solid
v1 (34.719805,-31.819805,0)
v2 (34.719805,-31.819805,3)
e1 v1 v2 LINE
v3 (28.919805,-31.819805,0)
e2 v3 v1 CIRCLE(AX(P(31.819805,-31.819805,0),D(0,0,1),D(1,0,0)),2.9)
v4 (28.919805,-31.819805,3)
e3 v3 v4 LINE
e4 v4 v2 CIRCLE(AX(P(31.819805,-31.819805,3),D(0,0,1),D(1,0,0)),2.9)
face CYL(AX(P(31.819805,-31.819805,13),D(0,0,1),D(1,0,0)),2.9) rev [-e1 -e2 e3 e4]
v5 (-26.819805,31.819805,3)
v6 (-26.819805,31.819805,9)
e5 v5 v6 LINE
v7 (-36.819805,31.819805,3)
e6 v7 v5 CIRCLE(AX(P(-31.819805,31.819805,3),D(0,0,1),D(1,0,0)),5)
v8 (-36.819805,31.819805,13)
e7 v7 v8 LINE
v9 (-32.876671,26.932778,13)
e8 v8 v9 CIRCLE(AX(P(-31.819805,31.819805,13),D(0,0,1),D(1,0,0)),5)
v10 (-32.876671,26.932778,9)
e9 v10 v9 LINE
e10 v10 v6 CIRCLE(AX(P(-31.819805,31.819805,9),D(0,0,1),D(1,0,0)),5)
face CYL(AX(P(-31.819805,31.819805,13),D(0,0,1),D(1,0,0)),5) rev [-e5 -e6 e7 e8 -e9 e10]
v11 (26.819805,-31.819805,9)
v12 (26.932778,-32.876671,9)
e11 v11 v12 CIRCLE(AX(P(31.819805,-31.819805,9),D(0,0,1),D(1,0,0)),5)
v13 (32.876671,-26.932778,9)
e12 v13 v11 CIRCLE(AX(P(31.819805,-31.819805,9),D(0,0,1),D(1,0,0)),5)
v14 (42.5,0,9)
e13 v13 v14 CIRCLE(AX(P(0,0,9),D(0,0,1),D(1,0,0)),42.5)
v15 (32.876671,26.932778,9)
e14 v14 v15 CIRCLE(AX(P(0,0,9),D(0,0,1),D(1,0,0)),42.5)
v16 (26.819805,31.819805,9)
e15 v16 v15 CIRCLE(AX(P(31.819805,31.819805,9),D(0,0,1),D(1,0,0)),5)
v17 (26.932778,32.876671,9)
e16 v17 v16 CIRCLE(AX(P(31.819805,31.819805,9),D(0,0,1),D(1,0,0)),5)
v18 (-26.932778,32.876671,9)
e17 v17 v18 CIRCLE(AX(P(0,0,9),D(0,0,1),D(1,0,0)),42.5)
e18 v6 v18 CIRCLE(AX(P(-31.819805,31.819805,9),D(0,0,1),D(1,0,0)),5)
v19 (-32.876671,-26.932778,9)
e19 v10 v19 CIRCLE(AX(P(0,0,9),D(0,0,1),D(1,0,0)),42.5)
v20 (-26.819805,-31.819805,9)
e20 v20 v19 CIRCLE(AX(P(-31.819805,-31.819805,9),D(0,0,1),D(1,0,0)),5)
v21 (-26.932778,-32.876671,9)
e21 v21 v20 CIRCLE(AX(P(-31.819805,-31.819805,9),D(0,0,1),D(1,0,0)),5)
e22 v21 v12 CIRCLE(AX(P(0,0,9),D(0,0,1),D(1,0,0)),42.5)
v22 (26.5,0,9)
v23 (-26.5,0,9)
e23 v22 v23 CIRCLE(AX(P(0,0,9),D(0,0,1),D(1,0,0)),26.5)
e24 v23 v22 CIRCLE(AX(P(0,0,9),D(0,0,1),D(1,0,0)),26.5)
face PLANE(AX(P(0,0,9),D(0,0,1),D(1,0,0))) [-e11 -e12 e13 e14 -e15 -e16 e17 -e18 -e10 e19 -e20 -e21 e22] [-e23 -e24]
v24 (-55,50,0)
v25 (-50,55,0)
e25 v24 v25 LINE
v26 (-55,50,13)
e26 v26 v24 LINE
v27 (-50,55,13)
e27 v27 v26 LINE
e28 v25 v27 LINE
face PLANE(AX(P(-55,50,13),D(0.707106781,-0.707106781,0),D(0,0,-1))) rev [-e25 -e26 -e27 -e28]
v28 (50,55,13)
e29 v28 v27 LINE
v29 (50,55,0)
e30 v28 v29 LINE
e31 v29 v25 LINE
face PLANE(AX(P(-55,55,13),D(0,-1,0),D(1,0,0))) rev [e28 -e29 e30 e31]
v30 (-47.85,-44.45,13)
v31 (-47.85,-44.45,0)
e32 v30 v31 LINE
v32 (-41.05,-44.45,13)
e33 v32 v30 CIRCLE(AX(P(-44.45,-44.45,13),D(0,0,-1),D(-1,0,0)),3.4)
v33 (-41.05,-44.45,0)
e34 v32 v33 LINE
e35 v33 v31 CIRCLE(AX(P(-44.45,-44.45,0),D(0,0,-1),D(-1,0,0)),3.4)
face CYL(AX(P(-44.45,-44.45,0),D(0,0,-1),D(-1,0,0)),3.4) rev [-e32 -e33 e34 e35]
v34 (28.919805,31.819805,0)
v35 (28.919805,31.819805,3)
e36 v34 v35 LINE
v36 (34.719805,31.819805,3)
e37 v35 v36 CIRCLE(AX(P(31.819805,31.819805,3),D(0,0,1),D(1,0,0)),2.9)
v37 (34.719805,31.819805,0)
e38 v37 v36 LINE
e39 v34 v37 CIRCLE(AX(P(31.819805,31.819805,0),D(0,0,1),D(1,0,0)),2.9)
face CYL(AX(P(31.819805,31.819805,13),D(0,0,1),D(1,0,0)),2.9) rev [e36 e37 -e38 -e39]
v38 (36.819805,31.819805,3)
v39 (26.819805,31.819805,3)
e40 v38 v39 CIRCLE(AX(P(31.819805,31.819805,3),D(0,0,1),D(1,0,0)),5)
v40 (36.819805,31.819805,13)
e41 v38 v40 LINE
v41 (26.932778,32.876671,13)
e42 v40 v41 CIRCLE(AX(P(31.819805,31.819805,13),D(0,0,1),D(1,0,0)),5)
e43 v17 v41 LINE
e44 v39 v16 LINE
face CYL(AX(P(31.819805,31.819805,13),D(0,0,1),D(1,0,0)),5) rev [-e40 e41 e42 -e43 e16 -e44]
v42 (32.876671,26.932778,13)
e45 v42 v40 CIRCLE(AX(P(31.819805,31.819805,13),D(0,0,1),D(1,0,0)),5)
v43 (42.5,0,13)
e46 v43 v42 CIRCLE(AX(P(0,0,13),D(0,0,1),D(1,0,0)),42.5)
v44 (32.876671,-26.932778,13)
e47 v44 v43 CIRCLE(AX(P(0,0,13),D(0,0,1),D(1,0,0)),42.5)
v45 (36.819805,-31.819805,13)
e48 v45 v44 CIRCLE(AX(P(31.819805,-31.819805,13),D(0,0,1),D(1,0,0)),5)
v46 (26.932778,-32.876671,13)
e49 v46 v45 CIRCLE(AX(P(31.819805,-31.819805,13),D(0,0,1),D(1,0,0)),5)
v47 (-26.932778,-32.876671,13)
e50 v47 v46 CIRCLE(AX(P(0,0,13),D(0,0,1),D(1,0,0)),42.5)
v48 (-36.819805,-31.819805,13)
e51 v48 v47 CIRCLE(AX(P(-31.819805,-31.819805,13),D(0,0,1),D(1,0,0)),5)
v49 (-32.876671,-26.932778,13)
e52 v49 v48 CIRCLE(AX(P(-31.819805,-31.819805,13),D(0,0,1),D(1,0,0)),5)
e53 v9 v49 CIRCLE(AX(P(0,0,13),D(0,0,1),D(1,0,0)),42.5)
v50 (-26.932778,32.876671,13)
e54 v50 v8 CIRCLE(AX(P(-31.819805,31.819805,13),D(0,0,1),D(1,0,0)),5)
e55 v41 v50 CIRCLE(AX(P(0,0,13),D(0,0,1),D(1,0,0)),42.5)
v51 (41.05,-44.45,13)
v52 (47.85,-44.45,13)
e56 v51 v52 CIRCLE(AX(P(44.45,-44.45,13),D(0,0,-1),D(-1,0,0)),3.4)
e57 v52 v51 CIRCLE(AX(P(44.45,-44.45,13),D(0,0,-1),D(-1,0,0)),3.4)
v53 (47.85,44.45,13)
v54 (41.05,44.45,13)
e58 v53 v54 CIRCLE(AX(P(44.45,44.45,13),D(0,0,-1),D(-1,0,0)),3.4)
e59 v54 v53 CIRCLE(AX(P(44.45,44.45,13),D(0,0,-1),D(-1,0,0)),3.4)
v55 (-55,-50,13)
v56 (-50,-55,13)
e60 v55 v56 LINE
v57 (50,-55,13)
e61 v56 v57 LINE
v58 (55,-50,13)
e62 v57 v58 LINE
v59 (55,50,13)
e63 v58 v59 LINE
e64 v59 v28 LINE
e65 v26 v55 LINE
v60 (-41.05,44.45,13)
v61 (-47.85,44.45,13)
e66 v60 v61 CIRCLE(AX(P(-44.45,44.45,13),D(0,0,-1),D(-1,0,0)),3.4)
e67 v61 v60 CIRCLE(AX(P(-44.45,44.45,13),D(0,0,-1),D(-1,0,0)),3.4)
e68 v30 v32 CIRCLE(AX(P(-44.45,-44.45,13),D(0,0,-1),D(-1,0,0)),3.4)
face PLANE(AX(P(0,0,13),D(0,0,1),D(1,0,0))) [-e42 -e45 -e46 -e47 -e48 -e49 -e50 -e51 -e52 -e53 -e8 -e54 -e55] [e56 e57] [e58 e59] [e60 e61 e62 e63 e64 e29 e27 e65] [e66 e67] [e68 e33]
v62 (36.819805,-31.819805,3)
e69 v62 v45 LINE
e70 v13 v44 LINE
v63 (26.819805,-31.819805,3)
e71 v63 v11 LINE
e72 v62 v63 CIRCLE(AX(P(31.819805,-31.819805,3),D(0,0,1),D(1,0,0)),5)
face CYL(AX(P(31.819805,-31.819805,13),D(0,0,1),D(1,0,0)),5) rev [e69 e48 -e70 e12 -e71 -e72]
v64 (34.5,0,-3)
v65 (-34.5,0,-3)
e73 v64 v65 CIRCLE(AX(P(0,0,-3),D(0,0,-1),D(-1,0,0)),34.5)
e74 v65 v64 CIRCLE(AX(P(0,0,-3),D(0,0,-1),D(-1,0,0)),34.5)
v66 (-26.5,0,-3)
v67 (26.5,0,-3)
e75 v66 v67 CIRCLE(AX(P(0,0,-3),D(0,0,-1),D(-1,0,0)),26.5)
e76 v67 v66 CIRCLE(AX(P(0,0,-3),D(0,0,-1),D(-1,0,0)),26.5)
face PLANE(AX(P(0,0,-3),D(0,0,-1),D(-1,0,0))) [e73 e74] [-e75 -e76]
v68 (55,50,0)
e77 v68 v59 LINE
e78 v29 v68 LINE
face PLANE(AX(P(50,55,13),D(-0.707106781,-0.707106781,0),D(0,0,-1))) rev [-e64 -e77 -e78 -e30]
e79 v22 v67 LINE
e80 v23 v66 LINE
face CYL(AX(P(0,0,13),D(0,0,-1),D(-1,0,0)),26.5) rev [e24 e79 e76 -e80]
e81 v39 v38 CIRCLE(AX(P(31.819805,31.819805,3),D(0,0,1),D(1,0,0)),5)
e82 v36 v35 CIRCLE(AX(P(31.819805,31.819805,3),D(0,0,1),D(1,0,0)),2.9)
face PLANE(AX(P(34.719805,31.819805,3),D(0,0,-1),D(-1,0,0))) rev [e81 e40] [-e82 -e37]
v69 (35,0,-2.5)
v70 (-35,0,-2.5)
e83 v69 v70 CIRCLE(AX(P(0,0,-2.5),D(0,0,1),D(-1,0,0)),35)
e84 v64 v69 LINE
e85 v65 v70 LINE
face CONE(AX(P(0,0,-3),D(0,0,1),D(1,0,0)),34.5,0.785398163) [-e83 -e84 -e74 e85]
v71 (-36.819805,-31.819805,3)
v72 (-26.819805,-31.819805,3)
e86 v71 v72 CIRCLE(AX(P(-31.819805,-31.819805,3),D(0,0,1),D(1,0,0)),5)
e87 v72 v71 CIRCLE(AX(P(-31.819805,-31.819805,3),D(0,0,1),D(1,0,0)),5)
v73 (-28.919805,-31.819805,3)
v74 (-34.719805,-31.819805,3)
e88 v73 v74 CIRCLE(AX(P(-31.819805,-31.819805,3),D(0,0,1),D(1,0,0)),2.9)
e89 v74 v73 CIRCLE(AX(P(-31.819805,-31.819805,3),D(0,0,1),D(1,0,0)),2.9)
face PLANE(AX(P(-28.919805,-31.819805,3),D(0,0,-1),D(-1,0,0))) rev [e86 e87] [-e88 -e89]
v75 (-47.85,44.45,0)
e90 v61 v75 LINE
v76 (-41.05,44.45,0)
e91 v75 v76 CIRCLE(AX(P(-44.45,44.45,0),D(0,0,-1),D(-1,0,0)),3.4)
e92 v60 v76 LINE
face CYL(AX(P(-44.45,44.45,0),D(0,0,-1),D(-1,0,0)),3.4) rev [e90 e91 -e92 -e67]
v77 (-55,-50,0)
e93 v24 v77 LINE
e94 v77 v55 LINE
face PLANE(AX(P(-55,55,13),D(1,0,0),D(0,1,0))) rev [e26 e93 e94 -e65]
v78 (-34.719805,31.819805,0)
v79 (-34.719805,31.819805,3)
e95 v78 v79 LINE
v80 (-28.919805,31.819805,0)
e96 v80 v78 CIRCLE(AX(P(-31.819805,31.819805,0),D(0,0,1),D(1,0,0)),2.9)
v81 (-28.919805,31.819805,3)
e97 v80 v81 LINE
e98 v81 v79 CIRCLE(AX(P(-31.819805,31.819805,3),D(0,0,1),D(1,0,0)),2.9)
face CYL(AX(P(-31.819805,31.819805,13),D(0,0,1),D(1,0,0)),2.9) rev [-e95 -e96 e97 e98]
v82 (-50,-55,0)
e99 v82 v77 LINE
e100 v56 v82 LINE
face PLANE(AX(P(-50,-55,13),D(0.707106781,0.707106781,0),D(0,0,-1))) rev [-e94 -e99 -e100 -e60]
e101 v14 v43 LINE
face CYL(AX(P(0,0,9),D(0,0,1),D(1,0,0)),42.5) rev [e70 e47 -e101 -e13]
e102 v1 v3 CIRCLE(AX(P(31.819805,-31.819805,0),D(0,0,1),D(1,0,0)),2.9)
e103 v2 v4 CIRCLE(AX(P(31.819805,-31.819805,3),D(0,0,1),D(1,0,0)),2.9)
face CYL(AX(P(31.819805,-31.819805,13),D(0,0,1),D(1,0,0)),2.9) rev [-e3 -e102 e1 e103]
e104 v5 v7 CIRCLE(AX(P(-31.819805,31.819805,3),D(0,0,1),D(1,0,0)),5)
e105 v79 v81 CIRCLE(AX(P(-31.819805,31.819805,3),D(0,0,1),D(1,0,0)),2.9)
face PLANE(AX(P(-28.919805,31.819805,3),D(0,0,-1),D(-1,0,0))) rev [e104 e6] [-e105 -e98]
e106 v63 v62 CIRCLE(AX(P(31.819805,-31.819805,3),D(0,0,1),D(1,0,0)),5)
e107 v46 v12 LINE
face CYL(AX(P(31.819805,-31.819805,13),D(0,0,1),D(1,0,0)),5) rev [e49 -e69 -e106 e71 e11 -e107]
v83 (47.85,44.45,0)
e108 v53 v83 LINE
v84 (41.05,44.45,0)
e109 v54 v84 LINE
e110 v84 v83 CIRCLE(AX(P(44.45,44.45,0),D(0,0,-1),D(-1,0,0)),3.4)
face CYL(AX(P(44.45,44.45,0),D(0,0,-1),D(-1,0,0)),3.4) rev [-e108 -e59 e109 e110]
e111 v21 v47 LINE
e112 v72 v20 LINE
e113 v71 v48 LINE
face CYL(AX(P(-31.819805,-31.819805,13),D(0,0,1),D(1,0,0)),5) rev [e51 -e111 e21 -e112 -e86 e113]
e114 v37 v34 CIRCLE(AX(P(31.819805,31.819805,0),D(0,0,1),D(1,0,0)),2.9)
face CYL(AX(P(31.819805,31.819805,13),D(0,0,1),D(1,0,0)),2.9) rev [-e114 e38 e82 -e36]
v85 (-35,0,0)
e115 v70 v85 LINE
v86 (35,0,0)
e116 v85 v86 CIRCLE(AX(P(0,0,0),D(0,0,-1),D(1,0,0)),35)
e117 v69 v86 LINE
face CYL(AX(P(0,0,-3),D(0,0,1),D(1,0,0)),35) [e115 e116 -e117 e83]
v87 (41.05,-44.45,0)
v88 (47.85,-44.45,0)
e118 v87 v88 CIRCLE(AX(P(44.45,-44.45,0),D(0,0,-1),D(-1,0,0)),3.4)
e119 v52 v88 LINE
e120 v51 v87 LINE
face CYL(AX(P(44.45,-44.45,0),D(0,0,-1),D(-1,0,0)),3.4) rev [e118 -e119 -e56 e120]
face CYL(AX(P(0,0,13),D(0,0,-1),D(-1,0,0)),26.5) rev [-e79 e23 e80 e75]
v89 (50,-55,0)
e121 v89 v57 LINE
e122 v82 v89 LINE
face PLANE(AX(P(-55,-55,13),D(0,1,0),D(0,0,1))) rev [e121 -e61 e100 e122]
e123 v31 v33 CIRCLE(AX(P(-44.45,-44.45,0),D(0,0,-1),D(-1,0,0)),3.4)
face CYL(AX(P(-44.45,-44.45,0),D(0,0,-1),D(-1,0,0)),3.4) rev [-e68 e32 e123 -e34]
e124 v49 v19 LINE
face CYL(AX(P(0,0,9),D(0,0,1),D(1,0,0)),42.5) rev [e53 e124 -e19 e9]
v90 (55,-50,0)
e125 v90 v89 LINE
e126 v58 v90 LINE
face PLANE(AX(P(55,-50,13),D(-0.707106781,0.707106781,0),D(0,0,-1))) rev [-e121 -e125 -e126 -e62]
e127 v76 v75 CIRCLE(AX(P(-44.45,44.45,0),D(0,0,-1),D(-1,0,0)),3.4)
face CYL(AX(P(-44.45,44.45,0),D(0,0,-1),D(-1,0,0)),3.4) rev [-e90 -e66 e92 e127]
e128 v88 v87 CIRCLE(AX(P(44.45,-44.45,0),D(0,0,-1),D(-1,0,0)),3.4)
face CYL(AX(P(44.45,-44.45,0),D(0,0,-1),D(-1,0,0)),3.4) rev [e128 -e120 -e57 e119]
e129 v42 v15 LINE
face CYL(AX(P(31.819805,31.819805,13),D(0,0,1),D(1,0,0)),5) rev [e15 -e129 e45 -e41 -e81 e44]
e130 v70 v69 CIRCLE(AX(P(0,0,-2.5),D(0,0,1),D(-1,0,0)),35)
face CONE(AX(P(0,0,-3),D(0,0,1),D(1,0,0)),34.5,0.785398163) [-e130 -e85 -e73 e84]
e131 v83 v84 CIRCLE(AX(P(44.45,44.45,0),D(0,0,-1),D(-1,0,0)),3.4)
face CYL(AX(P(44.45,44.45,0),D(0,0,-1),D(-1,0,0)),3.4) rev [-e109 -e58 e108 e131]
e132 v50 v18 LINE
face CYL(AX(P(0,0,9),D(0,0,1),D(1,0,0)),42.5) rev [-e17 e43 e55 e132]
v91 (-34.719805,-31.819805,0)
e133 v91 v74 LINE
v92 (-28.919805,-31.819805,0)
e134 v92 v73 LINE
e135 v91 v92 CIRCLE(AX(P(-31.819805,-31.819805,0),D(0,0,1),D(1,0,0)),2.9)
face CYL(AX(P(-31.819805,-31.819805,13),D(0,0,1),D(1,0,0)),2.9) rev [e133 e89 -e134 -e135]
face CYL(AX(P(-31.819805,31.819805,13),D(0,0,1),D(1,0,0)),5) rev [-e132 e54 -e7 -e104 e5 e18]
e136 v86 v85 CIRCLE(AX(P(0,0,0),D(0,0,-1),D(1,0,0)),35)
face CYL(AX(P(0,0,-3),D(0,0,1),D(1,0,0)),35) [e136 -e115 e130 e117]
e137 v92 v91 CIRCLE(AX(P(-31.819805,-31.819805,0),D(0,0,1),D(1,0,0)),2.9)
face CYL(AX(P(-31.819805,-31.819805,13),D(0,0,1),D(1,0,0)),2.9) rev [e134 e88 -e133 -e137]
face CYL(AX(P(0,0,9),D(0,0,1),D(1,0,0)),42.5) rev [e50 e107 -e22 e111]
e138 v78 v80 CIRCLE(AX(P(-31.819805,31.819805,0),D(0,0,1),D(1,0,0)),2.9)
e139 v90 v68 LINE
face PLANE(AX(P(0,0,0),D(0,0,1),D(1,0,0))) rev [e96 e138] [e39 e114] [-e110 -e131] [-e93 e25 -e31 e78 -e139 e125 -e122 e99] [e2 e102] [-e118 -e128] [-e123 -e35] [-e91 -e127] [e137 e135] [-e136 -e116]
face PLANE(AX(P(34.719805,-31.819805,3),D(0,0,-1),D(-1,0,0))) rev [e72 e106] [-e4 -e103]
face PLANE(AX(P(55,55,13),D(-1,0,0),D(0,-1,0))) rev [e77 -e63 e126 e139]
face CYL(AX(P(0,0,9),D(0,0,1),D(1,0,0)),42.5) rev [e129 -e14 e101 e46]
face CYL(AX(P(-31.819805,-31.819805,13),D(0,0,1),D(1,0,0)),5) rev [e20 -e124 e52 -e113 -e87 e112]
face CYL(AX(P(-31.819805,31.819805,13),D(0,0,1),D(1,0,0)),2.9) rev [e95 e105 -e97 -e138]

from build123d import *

# Parameters (mm, degrees)
SKETCH_1_W                   = 110
SKETCH_1_H                   = 110
EXTRUDE_1_DEPTH              = 13
SKETCH_2_R                   = 42.5
CUT_EXTRUDE_1_DEPTH          = 4
SKETCH_3_R                   = 26.5
CUT_EXTRUDE_2_DEPTH          = 79.860636569
EXTRUDE_START                = 3
SKETCH_4_R                   = 35
SKETCH_4_R_2                 = 26.5
EXTRUDE_2_DEPTH              = 3
HOLE_WIZARD_M8_1_D           = 6.8
CHAMFER_1_SIZE               = 5
HOLE_WIZARD_M5_1_D           = 5.8
HOLE_WIZARD_M5_1_CBORE_D     = 10
HOLE_WIZARD_M5_1_CBORE_DEPTH = 10
CHAMFER_2_SIZE               = 0.5


with BuildPart() as part:
    # 草图1 → 凸台-拉伸1 (new body)
    with BuildSketch(Plane.XY):
        Rectangle(SKETCH_1_W, SKETCH_1_H)
    extrude(amount=EXTRUDE_1_DEPTH)

    # 草图2 → 切除-拉伸1 (cut)
    with BuildSketch(Plane.XY.offset(13)):
        Circle(SKETCH_2_R)
    extrude(amount=-CUT_EXTRUDE_1_DEPTH, mode=Mode.SUBTRACT)

    # 草图3 → 切除-拉伸2 (cut, through all)
    with BuildSketch(Plane(origin=(0, 0, 0), x_dir=(-1, 0, 0), z_dir=(0, 0, -1))):
        Circle(SKETCH_3_R)
    extrude(amount=-CUT_EXTRUDE_2_DEPTH, mode=Mode.SUBTRACT)

    # 草图4 → 凸台-拉伸2 (add)
    with BuildSketch(Plane(origin=(0, 0, 0), x_dir=(-1, 0, 0), z_dir=(0, 0, -1)).offset(EXTRUDE_START)):
        with Locations(Location((0, 0, 0), (0, 0, 180))):
            Circle(SKETCH_4_R)
        Circle(SKETCH_4_R_2, mode=Mode.SUBTRACT)
    extrude(amount=-EXTRUDE_2_DEPTH)

    # M8 螺纹孔1 (through all)
    with Locations(Plane(origin=(0, 0, 0), x_dir=(-1, 0, 0), z_dir=(0, 0, -1))):
        with Locations((-44.45, 44.45), (44.45, 44.45), (44.45, -44.45), (-44.45, -44.45)):
            Hole(HOLE_WIZARD_M8_1_D / 2)

    # 倒角1
    chamfer_1_edges = [part.edges().sort_by_distance(p)[0] for p in [
        (55, -55, 6.5),
        (-55, -55, 6.5),
        (-55, 55, 6.5),
        (55, 55, 6.5),
    ]]
    chamfer(chamfer_1_edges, length=CHAMFER_1_SIZE)

    # M5 六角凹头螺钉的柱形沉头孔1 (through all)
    with Locations(Plane.XY.offset(13)):
        with Locations((-31.819805153, 31.819805153), (-31.819805153, -31.819805153), (31.819805153, -31.819805153), (31.819805153, 31.819805153)):
            CounterBoreHole(HOLE_WIZARD_M5_1_D / 2, HOLE_WIZARD_M5_1_CBORE_D / 2, HOLE_WIZARD_M5_1_CBORE_DEPTH)

    # 倒角2
    chamfer_2_edges = [part.edges().sort_by_distance(p)[0] for p in [
        (-35, 0, -3),
    ]]
    chamfer(chamfer_2_edges, length=CHAMFER_2_SIZE)


solid = part.part
